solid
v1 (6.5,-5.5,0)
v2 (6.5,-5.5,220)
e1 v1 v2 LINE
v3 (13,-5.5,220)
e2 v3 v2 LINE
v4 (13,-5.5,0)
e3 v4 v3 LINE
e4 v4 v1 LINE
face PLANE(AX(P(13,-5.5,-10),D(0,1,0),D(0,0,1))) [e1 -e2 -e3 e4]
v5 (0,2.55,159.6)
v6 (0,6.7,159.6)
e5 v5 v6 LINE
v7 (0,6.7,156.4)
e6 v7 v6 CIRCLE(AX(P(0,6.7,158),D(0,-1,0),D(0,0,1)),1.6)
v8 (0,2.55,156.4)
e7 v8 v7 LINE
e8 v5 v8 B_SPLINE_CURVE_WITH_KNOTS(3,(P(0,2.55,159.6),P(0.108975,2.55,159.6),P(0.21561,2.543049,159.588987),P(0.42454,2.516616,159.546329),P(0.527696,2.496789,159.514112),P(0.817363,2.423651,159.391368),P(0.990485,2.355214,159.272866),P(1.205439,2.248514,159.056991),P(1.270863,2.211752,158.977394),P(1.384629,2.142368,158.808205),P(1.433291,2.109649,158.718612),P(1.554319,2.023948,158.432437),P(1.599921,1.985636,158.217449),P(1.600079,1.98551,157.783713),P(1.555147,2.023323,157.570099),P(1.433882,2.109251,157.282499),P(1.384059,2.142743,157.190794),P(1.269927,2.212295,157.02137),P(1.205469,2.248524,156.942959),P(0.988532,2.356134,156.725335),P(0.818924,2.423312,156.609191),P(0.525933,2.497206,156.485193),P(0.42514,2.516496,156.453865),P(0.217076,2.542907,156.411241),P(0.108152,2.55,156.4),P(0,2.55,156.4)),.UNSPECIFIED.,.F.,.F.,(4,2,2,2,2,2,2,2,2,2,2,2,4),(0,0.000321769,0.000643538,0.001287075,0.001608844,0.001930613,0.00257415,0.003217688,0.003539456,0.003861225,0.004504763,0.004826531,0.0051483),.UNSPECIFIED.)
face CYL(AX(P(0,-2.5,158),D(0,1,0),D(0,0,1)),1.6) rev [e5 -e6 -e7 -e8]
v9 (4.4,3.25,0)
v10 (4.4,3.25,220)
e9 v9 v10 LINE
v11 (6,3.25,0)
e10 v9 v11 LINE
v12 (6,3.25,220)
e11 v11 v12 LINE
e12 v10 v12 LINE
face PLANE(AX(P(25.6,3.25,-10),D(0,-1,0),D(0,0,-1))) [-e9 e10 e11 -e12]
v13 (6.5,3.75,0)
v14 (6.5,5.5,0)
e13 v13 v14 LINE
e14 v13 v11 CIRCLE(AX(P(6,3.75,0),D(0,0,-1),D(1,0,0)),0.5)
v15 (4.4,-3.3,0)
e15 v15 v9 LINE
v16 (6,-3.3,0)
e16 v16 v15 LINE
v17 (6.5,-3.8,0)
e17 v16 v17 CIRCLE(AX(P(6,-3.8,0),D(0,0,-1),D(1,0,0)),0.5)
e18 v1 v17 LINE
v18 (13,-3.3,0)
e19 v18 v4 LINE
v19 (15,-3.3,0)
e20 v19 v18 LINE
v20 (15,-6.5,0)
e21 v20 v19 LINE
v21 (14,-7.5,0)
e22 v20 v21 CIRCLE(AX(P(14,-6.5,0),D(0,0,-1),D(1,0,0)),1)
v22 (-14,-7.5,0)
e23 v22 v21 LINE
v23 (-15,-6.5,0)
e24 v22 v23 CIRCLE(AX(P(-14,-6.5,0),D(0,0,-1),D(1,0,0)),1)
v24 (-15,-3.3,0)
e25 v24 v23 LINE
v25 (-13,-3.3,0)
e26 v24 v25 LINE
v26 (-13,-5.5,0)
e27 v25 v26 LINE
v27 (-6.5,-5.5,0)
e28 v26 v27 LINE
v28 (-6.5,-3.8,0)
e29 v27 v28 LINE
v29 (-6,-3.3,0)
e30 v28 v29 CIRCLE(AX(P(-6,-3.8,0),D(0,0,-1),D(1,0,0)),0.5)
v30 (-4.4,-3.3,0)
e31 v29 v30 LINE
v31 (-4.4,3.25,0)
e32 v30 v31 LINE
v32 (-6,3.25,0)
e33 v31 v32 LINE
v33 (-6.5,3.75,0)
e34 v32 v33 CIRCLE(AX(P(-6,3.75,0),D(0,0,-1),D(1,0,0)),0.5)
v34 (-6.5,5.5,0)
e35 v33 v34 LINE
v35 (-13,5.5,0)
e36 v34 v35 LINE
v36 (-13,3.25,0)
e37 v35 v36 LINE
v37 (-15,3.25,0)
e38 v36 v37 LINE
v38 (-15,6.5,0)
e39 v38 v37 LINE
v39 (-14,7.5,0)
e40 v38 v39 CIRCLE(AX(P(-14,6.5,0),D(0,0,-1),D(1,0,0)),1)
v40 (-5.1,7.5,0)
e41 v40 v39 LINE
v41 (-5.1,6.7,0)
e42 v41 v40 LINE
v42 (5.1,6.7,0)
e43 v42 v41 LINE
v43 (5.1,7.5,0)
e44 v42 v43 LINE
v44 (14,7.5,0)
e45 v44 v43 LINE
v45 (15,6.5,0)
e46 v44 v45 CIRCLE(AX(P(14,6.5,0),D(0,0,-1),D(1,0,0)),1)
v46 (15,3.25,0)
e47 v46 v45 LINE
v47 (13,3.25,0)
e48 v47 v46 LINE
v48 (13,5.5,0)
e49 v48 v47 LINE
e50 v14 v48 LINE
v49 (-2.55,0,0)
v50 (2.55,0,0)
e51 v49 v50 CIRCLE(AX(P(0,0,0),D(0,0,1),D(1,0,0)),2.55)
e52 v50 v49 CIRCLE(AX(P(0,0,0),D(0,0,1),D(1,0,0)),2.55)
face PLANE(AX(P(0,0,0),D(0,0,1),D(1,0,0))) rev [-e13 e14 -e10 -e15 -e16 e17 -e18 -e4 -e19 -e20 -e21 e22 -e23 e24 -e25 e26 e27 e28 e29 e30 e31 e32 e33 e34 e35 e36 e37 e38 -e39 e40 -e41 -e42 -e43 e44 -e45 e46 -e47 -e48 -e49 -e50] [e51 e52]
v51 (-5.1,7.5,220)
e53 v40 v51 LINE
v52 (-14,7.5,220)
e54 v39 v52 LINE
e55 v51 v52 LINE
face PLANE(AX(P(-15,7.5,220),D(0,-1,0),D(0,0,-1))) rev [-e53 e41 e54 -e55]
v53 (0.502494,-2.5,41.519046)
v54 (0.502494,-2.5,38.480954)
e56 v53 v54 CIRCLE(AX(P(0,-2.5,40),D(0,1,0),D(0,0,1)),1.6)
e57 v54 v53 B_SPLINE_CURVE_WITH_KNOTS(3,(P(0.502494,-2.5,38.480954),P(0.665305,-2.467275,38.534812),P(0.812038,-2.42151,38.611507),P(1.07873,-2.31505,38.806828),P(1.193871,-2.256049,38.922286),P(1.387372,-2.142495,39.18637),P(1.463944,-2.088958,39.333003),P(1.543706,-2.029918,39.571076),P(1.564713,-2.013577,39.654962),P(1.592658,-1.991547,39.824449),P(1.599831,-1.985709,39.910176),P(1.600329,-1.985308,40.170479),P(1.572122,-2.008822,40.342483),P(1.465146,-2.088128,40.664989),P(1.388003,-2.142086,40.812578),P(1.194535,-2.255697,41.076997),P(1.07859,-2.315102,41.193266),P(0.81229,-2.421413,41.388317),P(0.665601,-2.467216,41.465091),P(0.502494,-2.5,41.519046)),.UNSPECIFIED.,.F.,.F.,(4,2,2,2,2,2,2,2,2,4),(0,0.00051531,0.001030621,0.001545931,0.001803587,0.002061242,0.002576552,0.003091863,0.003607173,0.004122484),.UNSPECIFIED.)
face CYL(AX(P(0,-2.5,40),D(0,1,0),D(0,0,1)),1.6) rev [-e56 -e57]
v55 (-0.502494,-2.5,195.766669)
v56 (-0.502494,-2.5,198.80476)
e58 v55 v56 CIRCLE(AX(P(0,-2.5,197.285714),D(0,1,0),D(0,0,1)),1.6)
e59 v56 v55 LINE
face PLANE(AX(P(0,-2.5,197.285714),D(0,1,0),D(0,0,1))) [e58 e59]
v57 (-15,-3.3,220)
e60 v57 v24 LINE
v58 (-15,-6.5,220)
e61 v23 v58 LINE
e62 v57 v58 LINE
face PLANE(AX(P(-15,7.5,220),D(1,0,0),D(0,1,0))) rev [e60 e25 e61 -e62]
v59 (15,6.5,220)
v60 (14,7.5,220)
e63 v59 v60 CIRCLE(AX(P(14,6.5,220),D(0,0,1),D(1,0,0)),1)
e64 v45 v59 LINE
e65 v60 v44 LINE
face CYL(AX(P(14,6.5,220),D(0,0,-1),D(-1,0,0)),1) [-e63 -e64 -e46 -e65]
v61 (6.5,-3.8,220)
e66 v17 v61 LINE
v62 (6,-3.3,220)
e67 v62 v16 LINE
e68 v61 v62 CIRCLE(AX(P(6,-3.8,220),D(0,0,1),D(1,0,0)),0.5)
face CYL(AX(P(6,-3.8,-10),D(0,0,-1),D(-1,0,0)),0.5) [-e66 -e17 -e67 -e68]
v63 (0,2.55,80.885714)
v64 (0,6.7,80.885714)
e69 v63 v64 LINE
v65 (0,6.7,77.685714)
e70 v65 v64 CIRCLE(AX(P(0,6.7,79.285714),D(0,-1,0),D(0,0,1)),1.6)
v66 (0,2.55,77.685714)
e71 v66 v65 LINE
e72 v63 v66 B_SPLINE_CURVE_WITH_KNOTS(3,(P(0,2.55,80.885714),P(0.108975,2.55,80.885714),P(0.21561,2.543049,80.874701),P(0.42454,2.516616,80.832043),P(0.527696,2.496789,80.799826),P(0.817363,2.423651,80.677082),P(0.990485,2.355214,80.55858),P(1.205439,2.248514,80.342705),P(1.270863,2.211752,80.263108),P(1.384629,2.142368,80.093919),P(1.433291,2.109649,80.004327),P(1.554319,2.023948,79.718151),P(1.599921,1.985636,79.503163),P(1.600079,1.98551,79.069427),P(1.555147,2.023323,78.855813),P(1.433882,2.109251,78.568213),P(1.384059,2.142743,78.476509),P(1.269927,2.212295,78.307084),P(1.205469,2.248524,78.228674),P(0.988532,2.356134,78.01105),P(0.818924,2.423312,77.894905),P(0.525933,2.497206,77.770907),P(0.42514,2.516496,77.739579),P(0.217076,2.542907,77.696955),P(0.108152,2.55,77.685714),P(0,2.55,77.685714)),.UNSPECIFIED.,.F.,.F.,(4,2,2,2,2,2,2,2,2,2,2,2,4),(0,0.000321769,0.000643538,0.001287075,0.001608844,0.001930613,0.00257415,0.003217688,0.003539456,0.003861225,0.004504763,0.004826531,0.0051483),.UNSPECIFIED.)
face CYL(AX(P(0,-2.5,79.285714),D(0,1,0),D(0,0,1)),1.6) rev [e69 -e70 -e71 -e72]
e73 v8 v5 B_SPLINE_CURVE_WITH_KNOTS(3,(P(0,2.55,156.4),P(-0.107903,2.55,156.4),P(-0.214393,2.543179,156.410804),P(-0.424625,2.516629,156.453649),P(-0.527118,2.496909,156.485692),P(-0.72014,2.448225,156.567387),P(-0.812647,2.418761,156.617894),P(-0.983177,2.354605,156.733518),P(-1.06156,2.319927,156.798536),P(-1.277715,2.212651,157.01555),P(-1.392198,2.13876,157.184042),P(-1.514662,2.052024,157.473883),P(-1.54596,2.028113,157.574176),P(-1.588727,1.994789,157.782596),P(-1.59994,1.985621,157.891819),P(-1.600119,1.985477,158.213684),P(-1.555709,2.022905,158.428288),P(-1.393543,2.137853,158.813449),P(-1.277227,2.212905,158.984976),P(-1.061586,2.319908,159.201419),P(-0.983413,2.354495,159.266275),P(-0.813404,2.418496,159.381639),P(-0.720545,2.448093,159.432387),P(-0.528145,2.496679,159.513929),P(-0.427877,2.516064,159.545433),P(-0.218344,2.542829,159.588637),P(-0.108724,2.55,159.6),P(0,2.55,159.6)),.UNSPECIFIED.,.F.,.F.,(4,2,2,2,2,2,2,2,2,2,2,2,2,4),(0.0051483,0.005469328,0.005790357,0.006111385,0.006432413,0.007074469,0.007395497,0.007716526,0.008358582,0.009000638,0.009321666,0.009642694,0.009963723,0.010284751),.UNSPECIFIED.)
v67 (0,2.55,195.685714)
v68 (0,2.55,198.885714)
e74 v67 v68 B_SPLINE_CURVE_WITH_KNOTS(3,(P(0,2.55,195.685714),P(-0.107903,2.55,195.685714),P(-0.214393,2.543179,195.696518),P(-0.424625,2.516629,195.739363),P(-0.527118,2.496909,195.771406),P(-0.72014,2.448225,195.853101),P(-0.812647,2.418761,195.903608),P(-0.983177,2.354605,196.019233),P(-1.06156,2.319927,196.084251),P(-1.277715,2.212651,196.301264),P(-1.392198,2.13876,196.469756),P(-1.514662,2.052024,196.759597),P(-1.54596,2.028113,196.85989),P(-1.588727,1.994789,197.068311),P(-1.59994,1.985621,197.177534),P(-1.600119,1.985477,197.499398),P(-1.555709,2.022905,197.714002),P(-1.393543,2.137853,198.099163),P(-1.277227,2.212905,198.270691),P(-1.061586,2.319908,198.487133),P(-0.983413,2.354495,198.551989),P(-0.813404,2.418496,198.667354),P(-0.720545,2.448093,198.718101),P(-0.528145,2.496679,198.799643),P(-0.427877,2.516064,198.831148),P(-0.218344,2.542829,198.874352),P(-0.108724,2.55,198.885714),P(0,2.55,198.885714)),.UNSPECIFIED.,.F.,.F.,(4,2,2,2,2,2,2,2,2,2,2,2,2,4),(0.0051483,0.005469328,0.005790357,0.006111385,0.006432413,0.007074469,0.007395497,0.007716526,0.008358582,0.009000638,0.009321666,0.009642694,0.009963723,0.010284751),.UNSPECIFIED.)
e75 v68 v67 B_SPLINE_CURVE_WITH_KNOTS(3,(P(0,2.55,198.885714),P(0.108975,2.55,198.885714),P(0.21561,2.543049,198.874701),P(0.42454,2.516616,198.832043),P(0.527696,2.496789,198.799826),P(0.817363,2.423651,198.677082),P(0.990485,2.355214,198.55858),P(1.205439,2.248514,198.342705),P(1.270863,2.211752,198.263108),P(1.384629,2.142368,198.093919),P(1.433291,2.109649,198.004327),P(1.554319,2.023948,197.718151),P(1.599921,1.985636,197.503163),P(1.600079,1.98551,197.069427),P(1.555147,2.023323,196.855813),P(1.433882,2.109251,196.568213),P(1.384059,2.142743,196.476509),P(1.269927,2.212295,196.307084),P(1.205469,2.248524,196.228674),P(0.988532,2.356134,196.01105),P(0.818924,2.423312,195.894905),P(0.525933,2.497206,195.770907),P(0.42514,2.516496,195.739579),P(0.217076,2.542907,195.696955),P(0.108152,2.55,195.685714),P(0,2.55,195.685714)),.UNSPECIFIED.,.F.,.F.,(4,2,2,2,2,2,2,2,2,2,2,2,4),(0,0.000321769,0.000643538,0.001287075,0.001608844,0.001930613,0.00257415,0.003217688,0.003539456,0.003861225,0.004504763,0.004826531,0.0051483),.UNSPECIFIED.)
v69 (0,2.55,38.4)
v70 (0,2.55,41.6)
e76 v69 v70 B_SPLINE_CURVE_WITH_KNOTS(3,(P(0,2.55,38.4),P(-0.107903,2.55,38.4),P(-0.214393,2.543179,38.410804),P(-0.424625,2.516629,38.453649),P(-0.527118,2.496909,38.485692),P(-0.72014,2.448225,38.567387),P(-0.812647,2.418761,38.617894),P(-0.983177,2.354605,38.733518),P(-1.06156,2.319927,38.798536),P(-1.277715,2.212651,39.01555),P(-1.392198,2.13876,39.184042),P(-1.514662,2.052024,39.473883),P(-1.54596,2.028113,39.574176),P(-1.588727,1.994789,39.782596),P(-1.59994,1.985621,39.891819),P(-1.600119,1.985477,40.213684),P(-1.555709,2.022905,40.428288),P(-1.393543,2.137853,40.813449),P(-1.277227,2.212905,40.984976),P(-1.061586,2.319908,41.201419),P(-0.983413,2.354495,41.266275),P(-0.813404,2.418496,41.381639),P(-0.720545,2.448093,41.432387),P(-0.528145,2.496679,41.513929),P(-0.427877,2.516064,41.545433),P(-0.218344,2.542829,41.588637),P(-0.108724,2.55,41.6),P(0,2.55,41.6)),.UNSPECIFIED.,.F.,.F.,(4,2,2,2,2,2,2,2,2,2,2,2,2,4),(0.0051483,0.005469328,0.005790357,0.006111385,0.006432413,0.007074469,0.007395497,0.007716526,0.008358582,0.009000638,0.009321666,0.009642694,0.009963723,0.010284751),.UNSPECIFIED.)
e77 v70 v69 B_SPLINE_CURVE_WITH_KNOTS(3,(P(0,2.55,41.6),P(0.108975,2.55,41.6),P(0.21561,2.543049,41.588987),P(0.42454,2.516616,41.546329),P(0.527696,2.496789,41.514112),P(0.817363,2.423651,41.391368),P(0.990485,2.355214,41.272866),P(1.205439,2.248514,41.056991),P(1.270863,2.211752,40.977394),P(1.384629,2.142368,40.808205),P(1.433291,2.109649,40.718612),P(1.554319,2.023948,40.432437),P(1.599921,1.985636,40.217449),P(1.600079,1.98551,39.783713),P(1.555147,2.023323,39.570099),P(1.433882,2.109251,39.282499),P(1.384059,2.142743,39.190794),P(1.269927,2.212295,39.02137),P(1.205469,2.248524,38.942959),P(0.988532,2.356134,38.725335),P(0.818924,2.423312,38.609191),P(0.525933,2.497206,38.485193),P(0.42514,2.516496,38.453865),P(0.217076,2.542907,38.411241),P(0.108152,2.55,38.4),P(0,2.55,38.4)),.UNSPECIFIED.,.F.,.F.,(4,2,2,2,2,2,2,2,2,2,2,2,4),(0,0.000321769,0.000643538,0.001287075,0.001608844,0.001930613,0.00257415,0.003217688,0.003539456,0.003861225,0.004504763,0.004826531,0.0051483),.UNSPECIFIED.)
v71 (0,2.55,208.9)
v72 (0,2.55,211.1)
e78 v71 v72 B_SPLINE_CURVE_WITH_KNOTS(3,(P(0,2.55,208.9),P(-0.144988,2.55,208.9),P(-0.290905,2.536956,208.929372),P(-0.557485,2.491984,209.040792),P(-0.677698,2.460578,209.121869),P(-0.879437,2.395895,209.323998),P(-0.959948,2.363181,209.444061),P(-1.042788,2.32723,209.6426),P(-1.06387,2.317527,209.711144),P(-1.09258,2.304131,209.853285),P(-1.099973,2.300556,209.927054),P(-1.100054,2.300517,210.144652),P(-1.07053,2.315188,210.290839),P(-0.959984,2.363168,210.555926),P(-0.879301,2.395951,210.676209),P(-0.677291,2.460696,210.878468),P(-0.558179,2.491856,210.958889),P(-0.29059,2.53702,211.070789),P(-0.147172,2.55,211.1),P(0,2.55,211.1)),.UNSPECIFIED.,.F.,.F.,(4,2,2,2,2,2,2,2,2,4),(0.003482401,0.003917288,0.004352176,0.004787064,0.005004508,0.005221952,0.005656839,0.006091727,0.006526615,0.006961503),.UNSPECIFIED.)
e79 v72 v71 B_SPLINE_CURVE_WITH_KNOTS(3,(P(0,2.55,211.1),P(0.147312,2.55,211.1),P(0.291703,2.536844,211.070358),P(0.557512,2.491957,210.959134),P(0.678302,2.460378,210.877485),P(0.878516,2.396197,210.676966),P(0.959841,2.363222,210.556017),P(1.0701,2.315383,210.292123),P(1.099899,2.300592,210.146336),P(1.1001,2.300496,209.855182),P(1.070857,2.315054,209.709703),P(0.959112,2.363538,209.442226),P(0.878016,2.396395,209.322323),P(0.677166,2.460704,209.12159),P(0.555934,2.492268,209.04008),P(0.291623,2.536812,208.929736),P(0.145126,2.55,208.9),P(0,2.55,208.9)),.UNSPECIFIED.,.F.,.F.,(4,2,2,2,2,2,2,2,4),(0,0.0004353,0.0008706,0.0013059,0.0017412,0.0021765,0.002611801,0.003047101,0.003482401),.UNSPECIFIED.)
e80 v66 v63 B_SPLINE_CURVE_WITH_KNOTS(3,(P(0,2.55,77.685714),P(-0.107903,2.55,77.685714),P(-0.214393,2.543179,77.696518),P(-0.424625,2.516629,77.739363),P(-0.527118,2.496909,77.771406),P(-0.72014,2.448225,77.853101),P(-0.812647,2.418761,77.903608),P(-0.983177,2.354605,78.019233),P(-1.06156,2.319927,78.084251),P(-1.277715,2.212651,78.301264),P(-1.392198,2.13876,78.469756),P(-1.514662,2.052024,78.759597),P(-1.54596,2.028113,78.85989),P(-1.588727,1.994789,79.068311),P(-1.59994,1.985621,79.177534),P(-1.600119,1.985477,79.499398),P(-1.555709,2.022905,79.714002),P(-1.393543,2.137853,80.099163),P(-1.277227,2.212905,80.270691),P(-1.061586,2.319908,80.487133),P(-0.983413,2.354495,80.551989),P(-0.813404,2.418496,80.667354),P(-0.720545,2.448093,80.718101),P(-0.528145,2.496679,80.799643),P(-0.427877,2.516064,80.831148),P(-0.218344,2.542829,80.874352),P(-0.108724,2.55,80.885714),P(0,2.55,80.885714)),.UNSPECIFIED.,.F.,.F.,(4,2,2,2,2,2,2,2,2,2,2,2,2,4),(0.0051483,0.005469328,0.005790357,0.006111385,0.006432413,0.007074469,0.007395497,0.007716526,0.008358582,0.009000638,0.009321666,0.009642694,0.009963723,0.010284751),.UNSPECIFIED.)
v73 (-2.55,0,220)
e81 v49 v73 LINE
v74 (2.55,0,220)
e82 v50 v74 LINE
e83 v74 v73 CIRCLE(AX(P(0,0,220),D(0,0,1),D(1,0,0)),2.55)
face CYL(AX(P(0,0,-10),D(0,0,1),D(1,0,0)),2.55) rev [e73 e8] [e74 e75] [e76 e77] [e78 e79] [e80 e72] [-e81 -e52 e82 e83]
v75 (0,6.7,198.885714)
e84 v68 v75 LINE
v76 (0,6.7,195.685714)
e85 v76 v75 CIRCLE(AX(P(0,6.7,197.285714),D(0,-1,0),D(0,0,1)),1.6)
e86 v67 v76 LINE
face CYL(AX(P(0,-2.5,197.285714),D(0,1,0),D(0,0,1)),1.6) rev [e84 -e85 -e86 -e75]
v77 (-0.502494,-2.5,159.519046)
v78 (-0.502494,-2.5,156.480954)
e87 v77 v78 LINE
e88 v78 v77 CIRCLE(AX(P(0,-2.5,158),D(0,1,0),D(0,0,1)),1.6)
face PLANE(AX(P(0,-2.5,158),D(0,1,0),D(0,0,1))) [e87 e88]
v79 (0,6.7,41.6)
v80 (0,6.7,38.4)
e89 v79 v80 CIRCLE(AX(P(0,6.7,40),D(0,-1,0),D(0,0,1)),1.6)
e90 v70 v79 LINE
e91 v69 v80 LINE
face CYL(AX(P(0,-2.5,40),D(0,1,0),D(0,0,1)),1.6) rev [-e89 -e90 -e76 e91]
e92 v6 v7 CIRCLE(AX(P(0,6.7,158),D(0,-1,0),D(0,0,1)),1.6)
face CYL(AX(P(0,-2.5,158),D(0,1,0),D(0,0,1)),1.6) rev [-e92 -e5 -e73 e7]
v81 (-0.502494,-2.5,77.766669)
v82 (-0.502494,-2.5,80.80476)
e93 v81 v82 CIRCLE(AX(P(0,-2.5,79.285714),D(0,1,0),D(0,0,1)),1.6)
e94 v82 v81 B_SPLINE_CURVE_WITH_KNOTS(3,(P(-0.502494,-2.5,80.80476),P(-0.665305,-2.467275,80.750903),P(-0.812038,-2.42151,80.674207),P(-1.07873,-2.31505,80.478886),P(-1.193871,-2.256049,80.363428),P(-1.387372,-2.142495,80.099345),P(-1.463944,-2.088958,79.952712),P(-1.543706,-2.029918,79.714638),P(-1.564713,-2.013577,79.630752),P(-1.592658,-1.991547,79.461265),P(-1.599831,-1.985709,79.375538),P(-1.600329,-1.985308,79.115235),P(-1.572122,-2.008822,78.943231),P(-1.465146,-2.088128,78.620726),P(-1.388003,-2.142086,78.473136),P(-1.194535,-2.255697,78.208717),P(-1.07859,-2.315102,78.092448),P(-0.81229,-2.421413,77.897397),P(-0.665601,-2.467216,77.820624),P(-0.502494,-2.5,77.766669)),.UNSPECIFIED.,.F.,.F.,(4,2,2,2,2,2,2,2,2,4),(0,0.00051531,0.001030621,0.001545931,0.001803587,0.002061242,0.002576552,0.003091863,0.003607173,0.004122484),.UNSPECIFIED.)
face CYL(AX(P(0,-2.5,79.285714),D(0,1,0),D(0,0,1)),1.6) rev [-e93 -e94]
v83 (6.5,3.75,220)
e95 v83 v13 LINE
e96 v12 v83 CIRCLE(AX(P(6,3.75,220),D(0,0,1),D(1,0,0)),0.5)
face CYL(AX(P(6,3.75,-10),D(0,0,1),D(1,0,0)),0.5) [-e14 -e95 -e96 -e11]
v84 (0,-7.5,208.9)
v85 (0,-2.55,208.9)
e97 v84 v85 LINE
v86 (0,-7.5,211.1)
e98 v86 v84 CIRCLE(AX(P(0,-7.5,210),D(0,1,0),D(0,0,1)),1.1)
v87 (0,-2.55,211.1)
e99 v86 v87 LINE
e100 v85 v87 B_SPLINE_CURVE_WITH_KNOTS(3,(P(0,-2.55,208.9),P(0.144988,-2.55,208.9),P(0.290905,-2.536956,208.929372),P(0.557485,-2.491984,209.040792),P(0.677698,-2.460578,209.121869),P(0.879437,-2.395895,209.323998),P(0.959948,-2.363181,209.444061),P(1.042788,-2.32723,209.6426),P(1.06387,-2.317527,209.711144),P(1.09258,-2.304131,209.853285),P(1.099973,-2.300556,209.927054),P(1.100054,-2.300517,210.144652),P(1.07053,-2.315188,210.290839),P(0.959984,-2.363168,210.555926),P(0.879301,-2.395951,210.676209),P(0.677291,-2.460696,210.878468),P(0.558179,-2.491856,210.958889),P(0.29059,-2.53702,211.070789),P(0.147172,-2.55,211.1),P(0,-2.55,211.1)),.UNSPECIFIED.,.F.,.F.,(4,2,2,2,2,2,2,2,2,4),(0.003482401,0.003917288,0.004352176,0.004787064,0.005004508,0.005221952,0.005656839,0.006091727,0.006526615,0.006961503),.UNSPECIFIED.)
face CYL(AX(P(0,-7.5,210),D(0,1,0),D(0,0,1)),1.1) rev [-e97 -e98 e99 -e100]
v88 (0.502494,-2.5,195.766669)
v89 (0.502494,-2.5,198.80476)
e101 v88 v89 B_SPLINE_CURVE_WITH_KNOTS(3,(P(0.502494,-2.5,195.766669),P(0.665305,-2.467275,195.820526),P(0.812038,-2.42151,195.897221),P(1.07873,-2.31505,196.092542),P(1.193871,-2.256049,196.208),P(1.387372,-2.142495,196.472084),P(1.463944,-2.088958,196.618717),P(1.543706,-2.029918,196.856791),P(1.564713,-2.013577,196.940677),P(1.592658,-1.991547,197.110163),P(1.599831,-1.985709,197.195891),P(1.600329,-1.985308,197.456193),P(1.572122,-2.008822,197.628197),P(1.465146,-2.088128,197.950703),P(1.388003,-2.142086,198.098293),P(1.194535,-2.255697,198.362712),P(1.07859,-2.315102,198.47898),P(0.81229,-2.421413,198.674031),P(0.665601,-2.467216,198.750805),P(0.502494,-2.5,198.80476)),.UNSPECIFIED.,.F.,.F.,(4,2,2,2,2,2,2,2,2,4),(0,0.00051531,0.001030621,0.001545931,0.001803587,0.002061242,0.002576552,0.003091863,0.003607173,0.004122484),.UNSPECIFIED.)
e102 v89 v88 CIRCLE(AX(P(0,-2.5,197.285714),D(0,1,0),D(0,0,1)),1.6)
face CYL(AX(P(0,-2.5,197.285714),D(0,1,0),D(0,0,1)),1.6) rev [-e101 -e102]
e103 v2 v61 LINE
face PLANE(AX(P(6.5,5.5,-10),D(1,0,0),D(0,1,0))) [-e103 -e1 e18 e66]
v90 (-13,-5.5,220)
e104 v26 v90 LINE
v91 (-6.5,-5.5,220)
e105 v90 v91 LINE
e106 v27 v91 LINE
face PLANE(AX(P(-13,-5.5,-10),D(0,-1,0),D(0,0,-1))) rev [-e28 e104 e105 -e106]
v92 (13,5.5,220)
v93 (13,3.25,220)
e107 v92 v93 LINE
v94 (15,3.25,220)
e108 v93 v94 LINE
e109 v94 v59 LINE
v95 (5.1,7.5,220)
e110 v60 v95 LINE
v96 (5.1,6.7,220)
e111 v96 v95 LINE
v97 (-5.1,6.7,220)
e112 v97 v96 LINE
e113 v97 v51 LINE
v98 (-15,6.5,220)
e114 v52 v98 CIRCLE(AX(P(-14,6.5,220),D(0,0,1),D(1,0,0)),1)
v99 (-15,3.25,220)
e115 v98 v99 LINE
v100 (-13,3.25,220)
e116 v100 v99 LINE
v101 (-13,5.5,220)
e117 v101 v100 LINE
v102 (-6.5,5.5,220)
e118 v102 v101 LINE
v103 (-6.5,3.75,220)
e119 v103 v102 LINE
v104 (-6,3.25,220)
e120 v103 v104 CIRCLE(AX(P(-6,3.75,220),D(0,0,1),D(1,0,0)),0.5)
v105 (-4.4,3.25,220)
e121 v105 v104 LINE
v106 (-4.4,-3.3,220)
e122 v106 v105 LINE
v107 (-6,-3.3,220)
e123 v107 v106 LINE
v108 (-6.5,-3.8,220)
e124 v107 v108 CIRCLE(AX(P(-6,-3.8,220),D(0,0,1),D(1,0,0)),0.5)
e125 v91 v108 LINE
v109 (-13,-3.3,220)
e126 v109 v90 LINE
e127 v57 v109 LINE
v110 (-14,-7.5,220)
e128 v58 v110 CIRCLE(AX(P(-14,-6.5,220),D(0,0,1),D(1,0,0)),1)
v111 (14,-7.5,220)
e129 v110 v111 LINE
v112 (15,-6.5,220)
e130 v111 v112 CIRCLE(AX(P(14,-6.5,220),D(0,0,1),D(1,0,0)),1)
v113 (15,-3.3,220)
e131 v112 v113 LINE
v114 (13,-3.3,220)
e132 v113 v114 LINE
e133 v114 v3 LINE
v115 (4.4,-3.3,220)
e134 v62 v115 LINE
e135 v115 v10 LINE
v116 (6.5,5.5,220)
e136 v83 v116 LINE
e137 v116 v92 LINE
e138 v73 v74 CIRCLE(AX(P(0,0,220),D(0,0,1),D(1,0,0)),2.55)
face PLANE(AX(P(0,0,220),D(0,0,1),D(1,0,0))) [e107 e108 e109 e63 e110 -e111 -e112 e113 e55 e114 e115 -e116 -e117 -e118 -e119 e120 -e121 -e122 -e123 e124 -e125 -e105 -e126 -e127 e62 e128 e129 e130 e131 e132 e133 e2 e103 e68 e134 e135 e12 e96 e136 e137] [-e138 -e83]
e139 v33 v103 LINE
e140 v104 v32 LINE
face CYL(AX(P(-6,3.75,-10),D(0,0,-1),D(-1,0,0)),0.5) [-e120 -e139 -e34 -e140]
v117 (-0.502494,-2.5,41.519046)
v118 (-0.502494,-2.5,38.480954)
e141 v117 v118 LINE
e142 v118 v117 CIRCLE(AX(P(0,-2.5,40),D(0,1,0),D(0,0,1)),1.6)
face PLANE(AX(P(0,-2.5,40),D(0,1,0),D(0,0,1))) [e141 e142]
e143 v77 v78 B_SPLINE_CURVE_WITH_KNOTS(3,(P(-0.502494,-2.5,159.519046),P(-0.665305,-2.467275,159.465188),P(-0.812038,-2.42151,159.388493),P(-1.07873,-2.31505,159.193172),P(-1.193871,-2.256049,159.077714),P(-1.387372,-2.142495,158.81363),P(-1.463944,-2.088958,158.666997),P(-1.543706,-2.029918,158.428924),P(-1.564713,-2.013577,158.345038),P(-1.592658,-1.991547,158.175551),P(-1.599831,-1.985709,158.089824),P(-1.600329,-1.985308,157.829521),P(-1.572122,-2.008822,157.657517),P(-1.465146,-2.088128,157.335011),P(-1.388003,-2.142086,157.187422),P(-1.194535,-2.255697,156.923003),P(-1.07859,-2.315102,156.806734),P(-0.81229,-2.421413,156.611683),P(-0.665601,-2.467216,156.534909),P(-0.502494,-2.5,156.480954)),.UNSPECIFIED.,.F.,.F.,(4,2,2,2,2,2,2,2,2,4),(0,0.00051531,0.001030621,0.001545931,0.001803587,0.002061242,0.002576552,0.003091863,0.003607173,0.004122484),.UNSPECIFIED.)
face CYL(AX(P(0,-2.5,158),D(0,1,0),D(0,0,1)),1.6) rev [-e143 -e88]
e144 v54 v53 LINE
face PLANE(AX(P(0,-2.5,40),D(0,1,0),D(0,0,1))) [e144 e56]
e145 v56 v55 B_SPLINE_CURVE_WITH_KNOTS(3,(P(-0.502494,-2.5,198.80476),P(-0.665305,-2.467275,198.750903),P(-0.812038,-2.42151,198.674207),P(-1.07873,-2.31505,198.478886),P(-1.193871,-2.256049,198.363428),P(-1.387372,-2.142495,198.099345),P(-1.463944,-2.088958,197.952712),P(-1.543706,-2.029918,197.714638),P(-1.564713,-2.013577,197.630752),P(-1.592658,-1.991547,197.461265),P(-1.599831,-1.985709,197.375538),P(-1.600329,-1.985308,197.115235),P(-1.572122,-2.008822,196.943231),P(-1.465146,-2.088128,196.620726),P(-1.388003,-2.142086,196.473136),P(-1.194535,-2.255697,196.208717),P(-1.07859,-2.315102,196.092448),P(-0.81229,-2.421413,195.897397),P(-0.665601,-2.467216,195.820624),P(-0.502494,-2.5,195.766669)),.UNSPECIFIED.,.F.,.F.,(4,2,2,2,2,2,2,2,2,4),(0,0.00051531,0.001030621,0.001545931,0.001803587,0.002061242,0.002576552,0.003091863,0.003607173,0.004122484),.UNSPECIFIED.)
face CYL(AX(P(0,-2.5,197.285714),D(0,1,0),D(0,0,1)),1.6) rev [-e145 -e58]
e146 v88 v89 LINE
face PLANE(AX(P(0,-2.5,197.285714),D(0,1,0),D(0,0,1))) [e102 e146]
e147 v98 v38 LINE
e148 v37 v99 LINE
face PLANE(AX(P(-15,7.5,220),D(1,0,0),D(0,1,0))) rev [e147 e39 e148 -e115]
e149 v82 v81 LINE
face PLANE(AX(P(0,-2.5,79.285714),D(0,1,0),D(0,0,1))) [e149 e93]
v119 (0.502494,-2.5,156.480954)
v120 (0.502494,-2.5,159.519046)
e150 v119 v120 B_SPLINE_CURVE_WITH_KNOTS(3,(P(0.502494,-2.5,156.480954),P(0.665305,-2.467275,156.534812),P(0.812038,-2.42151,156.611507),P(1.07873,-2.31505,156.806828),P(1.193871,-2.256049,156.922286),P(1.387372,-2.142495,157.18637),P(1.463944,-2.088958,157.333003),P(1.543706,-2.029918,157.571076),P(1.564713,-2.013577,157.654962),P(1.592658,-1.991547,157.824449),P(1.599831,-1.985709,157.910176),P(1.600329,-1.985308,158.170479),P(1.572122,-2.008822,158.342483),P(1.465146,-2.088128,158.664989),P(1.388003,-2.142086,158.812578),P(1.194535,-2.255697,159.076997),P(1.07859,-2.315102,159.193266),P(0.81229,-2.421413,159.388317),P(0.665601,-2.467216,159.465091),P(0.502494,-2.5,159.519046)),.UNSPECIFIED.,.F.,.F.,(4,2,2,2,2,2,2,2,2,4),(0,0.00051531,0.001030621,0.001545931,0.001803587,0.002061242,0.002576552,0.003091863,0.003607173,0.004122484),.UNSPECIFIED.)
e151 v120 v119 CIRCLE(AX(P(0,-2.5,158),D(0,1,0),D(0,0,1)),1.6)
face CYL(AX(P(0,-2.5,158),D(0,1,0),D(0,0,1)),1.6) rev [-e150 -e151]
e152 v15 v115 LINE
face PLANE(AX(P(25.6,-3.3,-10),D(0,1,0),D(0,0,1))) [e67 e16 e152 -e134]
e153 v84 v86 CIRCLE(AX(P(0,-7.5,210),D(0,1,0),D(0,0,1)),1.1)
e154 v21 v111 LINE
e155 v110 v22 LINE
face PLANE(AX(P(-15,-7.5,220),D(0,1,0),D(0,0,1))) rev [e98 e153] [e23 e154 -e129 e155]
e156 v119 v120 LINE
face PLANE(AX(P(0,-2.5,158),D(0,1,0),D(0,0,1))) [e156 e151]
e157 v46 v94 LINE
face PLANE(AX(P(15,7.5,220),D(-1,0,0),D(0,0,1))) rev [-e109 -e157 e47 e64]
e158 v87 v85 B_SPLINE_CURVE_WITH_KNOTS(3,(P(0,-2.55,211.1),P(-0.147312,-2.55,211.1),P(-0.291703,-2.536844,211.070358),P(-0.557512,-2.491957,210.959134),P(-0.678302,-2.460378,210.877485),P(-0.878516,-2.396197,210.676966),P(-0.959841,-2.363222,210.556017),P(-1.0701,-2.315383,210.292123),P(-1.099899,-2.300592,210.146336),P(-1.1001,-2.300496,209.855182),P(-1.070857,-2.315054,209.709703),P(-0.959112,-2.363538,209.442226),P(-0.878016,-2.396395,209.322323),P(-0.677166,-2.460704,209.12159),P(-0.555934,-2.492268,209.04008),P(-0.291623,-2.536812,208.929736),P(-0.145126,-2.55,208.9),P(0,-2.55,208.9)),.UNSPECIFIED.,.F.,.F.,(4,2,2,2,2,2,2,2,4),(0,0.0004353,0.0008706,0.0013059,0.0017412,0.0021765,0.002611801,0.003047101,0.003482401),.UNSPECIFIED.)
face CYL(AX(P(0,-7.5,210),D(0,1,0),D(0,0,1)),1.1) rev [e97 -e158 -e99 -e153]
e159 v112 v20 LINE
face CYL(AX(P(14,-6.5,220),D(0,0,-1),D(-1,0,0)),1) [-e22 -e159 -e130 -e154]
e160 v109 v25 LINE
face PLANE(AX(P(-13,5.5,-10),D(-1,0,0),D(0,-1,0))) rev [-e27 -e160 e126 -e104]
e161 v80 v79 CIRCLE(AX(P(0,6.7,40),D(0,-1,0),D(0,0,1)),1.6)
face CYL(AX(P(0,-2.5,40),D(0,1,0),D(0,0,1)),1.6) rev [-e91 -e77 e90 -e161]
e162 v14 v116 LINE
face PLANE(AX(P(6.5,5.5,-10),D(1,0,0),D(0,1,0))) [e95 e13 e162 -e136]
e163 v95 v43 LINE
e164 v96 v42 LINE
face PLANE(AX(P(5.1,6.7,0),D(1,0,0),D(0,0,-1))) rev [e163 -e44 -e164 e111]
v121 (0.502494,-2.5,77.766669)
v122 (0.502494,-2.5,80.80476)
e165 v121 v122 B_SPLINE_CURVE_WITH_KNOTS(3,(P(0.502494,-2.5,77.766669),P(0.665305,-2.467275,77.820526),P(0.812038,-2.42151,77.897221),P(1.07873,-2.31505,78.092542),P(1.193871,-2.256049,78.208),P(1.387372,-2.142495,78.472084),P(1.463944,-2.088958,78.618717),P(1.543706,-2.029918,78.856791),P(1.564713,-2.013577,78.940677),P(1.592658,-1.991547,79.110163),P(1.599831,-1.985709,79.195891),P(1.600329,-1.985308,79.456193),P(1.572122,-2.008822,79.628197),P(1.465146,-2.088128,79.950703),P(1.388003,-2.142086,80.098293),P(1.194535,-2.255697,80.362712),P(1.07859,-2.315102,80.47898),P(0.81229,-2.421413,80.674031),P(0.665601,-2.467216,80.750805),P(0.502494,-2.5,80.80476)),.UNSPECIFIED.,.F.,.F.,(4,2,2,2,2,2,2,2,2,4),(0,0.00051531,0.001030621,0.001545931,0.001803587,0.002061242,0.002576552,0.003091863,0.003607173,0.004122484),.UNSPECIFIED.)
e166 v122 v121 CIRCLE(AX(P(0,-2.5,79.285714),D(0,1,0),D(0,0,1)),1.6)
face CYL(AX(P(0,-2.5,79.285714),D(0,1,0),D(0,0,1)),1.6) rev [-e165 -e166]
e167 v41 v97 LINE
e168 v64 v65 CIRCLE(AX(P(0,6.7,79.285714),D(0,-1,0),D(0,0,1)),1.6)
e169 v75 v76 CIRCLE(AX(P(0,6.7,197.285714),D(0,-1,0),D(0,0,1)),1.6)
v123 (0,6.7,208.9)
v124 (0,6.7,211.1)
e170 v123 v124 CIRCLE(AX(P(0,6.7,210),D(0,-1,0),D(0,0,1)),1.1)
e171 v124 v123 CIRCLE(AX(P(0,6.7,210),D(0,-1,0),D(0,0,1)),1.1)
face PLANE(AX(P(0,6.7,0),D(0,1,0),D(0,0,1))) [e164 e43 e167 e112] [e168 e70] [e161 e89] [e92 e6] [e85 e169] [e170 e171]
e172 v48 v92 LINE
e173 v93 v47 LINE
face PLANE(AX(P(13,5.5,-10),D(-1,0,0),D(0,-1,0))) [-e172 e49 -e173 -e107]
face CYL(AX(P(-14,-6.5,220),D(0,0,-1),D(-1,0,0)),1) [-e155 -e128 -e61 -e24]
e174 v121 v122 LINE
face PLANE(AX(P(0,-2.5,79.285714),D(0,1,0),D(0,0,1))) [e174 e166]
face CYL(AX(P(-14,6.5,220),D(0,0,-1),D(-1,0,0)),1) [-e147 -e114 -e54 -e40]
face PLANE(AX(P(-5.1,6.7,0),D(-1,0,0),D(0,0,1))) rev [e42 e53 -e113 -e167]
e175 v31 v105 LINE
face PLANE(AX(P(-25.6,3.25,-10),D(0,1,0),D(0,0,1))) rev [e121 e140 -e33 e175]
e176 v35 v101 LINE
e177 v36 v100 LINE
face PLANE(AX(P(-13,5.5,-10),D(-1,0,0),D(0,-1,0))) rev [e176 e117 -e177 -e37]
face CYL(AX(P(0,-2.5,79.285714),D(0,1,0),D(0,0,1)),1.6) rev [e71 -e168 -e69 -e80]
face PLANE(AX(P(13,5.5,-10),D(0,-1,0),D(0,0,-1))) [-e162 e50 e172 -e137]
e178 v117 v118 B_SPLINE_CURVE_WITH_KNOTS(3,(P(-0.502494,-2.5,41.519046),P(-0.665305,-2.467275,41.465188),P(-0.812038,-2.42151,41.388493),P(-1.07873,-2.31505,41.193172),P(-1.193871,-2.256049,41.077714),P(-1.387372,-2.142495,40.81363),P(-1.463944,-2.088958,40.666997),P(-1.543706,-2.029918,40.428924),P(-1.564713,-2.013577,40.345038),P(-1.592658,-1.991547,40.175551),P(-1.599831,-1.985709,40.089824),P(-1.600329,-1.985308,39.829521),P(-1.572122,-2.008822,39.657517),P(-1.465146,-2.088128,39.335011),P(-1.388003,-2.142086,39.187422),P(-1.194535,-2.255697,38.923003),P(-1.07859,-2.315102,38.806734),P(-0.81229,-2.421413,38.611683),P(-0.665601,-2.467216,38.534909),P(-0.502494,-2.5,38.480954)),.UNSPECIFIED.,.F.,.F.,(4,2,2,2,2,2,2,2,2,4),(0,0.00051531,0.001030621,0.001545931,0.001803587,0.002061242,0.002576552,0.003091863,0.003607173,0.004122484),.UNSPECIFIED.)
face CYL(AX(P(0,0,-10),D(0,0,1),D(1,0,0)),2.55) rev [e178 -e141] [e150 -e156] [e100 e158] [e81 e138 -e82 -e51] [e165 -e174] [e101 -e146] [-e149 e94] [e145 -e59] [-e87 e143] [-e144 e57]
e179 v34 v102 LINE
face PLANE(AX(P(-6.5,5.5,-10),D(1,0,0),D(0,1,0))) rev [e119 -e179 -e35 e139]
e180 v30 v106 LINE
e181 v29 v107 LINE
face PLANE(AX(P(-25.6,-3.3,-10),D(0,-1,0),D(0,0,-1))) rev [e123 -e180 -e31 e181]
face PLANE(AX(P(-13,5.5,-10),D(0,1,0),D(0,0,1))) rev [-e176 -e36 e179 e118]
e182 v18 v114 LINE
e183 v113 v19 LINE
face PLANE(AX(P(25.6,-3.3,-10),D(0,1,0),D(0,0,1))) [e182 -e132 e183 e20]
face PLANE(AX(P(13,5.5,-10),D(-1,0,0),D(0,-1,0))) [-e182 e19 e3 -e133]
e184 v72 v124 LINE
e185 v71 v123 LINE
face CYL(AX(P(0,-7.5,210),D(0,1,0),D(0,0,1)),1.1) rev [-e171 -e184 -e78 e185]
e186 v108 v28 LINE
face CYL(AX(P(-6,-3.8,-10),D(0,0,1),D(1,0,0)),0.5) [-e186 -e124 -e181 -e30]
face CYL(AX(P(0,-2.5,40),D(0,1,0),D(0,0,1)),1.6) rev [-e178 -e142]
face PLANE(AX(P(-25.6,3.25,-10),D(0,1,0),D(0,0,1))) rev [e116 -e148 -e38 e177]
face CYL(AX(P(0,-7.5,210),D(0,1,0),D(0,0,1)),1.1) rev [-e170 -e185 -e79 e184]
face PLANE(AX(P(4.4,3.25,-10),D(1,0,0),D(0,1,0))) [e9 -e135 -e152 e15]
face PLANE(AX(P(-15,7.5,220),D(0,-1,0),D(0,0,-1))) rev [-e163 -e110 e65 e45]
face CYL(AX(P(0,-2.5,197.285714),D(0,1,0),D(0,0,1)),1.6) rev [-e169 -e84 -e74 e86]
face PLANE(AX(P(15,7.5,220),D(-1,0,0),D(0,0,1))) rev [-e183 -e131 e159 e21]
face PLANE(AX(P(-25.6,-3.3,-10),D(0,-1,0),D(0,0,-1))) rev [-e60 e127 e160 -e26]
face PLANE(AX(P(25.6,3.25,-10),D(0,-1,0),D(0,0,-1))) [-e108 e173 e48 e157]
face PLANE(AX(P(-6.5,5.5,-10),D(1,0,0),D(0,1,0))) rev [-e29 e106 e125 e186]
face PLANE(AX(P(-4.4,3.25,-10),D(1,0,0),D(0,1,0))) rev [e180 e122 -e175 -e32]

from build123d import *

# Parameters (mm, degrees)
SKETCH_1_W             = 30
SKETCH_1_H             = 15
EXTRUDE_1_DEPTH        = 220
FILLET_1_R             = 1
SKETCH_2_R             = 2.55
CUT_EXTRUDE_1_DEPTH    = 230
SKETCH_3_W             = 21.2
SKETCH_3_H             = 6.55
CUT_EXTRUDE_2_DEPTH    = 230
SKETCH_4_W             = 6.5
SKETCH_4_H             = 11
CUT_EXTRUDE_3_DEPTH    = 230
FILLET_2_R             = 0.5
SKETCH_5_R             = 1.6
CUT_EXTRUDE_4_DEPTH    = 10
PATTERN_LINEAR_1_COUNT = 2
PATTERN_LINEAR_1_PITCH = 118
SKETCH_6_R             = 1.1
CUT_EXTRUDE_5_DEPTH    = 222.020361153
SKETCH_7_W             = 10.2
SKETCH_7_H             = 220
CUT_EXTRUDE_6_DEPTH    = 0.8


with BuildPart() as part:
    # 草图1 → 凸台-拉伸1 (new body)
    with BuildSketch(Plane.XY):
        Rectangle(SKETCH_1_W, SKETCH_1_H)
    extrude(amount=EXTRUDE_1_DEPTH)

    # 圆角1
    fillet_1_edges = [part.edges().sort_by_distance(p)[0] for p in [
        (15, -7.5, 110),
        (-15, -7.5, 110),
        (-15, 7.5, 110),
        (15, 7.5, 110),
    ]]
    fillet(fillet_1_edges, radius=FILLET_1_R)

    # 草图2 → 切除-拉伸1 (cut)
    with BuildSketch(Plane.XY.offset(220)):
        Circle(SKETCH_2_R)
    extrude(amount=-CUT_EXTRUDE_1_DEPTH, mode=Mode.SUBTRACT)

    # 草图3 → 切除-拉伸2 (cut)
    with BuildSketch(Plane.XY.offset(220)):
        with Locations((-15, -0.025)):
            Rectangle(SKETCH_3_W, SKETCH_3_H)
    cut_extrude_2 = extrude(amount=-CUT_EXTRUDE_2_DEPTH, mode=Mode.SUBTRACT)

    # 镜向1: 切除-拉伸2 across plane
    add(cut_extrude_2.mirror(Plane(origin=(0, 0, 0), x_dir=(0, 0, 1), z_dir=(1, 0, 0))), mode=Mode.SUBTRACT)

    # 草图4 → 切除-拉伸3 (cut)
    with BuildSketch(Plane.XY.offset(220)):
        with Locations((-9.75, 0)):
            Rectangle(SKETCH_4_W, SKETCH_4_H)
    cut_extrude_3 = extrude(amount=-CUT_EXTRUDE_3_DEPTH, mode=Mode.SUBTRACT)

    # 镜向2: 切除-拉伸3 across plane
    add(cut_extrude_3.mirror(Plane(origin=(0, 0, 0), x_dir=(0, 0, 1), z_dir=(1, 0, 0))), mode=Mode.SUBTRACT)

    # 圆角2
    fillet_2_edges = [part.edges().sort_by_distance(p)[0] for p in [
        (6.5, -3.3, 110),
        (6.5, 3.25, 110),
        (-6.5, 3.25, 110),
        (-6.5, -3.3, 110),
    ]]
    fillet(fillet_2_edges, radius=FILLET_2_R)

    # 草图5 → 切除-拉伸4 (cut)
    with BuildSketch(Plane(origin=(0, 7.5, 0), x_dir=(1, 0, 0), z_dir=(0, 1, 0))):
        with Locations(Location((0, -40, 0), (0, 0, 270))):
            Circle(SKETCH_5_R)
        with Locations(Location((0, -79.285714286, 0), (0, 0, 270))):
            Circle(SKETCH_5_R)
    cut_extrude_4 = extrude(amount=-CUT_EXTRUDE_4_DEPTH, mode=Mode.SUBTRACT)

    # 阵列(线性)1: 切除-拉伸4 ×2
    with Locations(*[(0, 0, i * PATTERN_LINEAR_1_PITCH) for i in range(1, PATTERN_LINEAR_1_COUNT)]):
        add(cut_extrude_4, mode=Mode.SUBTRACT)

    # 草图6 → 切除-拉伸5 (cut, through all)
    with BuildSketch(Plane(origin=(0, 7.5, 0), x_dir=(1, 0, 0), z_dir=(0, 1, 0))):
        with Locations(Location((0, -210, 0), (0, 0, 270))):
            Circle(SKETCH_6_R)
    extrude(amount=-CUT_EXTRUDE_5_DEPTH, mode=Mode.SUBTRACT)

    # 草图7 → 切除-拉伸6 (cut)
    with BuildSketch(Plane(origin=(0, 7.5, 0), x_dir=(1, 0, 0), z_dir=(0, 1, 0))):
        with Locations((0, -110)):
            Rectangle(SKETCH_7_W, SKETCH_7_H)
    extrude(amount=-CUT_EXTRUDE_6_DEPTH, mode=Mode.SUBTRACT)


solid = part.part
